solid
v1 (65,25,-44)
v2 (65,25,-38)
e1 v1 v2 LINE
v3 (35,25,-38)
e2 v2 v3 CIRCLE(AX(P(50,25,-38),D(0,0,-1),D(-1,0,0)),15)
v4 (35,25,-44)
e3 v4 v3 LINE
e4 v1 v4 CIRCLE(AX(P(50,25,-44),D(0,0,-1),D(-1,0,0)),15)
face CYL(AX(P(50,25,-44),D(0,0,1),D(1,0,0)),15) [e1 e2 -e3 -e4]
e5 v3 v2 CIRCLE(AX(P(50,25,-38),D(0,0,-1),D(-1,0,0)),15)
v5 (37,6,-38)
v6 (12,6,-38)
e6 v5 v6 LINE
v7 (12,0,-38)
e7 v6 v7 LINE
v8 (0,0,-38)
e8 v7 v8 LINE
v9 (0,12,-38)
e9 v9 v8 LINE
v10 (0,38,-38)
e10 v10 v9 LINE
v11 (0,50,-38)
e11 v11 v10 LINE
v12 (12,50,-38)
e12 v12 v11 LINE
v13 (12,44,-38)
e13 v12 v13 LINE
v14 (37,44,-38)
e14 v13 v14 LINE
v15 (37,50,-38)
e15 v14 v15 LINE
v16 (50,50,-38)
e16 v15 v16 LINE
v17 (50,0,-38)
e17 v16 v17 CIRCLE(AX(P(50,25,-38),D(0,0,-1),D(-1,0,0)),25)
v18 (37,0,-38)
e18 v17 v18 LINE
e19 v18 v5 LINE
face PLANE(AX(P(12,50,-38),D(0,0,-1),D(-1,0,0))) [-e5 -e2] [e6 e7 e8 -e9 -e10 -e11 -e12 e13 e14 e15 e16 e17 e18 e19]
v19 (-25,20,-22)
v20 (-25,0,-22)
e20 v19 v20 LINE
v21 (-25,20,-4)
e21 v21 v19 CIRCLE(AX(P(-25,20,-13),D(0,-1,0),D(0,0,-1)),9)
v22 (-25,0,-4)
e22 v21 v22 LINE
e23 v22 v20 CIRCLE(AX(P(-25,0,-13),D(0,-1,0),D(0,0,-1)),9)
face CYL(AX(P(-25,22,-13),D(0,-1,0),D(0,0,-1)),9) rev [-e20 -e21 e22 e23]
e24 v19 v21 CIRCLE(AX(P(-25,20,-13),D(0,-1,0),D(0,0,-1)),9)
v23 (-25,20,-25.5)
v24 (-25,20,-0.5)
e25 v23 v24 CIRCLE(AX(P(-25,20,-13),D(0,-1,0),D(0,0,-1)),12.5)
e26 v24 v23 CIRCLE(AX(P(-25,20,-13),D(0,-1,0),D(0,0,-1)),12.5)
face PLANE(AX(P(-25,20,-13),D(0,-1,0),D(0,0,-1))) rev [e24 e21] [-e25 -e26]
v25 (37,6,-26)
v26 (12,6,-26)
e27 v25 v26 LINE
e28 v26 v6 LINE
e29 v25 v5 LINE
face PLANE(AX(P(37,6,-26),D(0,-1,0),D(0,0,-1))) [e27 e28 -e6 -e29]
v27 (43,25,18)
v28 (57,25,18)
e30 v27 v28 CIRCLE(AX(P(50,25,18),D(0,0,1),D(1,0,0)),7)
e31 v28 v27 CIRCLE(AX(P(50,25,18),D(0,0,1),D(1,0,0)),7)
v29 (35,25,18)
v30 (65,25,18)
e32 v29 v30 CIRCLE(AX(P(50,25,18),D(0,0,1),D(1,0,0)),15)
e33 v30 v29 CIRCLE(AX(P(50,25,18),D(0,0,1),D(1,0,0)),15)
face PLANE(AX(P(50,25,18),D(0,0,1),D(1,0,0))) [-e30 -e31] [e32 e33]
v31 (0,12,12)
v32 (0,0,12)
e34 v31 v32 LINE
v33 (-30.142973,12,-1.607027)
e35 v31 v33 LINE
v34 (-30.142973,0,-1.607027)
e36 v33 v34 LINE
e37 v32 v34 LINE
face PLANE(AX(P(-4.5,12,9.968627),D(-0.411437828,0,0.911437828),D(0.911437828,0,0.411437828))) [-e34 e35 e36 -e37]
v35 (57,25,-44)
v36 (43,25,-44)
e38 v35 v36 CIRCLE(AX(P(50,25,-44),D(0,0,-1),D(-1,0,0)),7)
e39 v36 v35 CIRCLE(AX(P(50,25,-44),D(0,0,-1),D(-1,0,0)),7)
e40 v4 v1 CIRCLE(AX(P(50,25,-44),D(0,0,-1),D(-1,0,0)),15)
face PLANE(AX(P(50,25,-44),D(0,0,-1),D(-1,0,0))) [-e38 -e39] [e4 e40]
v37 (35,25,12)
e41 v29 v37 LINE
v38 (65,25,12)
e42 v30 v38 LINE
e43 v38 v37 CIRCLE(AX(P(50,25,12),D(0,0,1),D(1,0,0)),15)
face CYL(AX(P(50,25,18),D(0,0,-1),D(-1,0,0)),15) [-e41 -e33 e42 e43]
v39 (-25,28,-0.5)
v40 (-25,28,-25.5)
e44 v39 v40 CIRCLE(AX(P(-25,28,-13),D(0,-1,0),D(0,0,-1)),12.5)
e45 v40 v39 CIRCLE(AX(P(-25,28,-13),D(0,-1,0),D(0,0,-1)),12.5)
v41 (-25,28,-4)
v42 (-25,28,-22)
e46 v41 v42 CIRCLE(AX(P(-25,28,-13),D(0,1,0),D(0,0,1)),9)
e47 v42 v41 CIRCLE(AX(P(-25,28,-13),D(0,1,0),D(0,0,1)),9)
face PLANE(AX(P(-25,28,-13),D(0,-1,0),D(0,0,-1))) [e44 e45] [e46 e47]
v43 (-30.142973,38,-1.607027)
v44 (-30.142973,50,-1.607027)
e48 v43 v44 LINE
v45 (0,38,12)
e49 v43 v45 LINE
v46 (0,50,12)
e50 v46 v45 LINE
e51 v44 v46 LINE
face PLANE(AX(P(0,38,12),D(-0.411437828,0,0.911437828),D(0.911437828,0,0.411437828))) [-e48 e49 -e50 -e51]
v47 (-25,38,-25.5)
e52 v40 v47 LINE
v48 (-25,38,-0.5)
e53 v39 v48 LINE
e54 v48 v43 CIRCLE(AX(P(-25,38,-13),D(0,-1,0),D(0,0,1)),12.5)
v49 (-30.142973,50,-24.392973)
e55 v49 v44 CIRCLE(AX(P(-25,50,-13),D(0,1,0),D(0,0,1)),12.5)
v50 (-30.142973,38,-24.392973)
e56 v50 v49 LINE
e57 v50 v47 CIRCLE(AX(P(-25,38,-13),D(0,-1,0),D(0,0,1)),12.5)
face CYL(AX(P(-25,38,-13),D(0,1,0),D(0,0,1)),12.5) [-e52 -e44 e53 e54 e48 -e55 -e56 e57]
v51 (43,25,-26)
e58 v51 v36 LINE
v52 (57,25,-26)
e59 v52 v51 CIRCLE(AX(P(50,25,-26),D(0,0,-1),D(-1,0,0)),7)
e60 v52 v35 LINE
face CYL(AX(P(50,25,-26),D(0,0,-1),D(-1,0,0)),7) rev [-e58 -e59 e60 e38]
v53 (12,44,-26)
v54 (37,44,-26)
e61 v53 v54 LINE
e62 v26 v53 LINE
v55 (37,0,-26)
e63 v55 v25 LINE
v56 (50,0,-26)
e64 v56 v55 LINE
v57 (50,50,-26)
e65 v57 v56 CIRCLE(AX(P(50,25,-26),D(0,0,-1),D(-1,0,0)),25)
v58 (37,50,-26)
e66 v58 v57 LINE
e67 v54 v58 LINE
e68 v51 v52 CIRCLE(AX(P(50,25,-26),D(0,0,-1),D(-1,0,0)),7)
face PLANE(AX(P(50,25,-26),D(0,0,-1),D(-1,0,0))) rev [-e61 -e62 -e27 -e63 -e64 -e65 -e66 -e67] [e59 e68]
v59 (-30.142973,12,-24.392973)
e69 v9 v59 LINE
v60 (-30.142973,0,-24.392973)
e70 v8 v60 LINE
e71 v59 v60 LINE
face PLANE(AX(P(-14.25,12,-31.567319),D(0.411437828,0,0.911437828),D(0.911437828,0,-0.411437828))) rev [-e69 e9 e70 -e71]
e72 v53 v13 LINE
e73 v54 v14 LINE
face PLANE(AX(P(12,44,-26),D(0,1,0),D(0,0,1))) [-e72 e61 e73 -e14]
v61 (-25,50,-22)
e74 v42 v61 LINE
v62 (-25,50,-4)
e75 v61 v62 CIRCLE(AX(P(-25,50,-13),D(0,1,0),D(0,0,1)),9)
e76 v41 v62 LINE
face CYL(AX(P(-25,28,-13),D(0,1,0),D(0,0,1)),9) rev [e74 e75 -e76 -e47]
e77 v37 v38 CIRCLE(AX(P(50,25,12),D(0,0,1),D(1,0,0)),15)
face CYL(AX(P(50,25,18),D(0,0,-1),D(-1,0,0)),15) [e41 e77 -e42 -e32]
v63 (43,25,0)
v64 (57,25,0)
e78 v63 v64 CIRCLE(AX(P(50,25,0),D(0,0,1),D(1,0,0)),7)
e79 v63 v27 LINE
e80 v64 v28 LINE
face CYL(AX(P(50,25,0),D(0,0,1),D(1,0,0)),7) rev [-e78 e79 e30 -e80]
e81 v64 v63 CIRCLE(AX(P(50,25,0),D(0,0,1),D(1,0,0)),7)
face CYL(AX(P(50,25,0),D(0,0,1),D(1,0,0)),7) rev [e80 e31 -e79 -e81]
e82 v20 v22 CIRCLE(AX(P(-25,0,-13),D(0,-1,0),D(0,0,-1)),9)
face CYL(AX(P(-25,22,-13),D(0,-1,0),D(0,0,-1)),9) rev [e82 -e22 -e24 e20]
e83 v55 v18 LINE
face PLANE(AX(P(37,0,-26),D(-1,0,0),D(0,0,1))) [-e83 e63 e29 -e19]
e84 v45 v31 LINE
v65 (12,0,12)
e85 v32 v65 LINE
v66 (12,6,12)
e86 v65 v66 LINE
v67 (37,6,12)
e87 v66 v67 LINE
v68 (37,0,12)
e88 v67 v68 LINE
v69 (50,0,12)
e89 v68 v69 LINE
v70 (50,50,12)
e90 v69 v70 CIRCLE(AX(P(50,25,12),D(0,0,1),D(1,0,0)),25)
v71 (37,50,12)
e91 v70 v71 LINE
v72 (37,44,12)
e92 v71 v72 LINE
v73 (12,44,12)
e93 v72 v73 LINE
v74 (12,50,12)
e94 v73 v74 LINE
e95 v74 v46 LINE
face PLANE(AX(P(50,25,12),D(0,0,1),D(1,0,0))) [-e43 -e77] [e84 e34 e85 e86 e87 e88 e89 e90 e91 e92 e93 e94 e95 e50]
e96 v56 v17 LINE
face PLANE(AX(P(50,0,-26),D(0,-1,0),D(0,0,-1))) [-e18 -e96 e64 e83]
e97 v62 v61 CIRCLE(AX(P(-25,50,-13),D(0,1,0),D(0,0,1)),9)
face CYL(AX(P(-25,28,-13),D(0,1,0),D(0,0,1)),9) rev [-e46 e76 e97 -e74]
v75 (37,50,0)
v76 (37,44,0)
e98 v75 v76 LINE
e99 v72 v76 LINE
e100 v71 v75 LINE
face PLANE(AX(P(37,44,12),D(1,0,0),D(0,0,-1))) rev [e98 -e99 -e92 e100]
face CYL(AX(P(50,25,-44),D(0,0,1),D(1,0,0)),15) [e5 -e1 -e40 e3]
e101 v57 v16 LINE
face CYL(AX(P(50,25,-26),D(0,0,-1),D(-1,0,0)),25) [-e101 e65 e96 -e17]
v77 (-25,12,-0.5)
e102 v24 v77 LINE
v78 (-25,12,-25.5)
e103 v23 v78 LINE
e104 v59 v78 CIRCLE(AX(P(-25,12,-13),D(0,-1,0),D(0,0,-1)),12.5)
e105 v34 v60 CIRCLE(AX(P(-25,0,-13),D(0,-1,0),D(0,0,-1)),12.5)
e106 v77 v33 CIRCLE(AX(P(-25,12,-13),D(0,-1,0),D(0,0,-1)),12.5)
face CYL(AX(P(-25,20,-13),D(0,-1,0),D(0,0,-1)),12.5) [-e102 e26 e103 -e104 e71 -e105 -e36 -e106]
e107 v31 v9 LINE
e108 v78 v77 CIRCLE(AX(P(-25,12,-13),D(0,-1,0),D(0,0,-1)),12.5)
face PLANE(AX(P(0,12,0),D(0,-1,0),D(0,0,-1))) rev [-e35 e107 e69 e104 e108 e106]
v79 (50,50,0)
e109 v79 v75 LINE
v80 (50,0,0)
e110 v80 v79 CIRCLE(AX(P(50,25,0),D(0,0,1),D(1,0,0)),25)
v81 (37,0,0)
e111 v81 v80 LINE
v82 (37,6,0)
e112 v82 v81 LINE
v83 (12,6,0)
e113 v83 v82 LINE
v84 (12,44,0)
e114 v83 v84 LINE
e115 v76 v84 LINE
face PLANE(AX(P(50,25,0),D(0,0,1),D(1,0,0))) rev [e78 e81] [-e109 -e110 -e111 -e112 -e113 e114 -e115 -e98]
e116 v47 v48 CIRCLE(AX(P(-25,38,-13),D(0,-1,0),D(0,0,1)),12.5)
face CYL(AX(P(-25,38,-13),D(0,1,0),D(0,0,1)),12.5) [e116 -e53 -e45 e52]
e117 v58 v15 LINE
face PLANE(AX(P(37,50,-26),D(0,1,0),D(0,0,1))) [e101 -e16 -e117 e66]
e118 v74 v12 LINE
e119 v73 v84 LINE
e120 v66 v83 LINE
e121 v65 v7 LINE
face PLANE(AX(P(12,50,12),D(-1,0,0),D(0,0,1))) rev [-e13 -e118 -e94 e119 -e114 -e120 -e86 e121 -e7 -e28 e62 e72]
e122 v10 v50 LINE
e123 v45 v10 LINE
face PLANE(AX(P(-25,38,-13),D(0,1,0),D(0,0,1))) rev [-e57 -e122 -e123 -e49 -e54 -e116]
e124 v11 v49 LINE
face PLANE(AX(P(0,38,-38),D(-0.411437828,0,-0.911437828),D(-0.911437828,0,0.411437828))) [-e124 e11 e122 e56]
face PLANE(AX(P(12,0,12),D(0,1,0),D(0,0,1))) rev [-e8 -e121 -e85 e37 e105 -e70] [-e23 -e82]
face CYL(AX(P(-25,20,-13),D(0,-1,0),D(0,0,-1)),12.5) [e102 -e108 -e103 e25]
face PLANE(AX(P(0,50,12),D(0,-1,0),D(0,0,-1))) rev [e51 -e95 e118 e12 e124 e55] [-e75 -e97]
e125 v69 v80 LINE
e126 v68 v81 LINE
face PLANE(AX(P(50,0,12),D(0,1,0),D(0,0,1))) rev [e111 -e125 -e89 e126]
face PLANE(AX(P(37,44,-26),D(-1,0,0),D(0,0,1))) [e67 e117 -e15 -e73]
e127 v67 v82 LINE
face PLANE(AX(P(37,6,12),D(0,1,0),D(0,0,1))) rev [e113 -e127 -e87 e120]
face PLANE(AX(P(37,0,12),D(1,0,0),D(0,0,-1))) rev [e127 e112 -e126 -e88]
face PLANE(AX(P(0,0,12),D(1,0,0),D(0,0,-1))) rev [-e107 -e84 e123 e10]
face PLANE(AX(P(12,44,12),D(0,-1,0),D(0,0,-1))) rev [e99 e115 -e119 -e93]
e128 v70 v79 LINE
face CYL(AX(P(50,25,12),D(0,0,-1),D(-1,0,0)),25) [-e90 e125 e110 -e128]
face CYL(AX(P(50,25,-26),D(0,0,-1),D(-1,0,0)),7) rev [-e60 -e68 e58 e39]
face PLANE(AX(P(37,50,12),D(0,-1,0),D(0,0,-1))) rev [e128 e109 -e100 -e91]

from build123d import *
from build123d.topology import SkipClean

# Parameters (mm, degrees)
MAIN_BODY_PLATE_DEPTH   = 12
UPPER_HUB_SKETCH_R      = 15
UPPER_HUB_30_DEPTH      = 6
SPACER_BLOCK_SKETCH_W   = 38
SPACER_BLOCK_SKETCH_H   = 50
SPACER_BLOCK_DEPTH      = 12
LOWER_LUG_DEPTH         = 12
LOWER_START             = 6
LOWER_HUB_SKETCH_R      = 15
LOWER_HUB_30_DEPTH      = 6
LOWER_PIN_BORE_SKETCH_R = 7
LOWER_PIN_BORE_14_DEPTH = 18
UPPER_START             = -18
UPPER_PIN_BORE_SKETCH_R = 7
UPPER_PIN_BORE_14_DEPTH = 18
CLEVIS_PLATE_DEPTH      = 12
CLEVIS_HUB_SKETCH_R     = 12.5
CLEVIS_HUB_25_DEPTH     = 10
CLEVIS_START            = -12
CLEVIS_WEB_DEPTH        = 12
CLEVIS_START_2          = -20
CLEVIS_LUG_SKETCH_R     = 12.5
CLEVIS_LUG_25_DEPTH     = 20
CLEVIS_BORE_A_SKETCH_R  = 9
CLEVIS_BORE_A_18_DEPTH  = 22
CLEVIS_START_3          = -22
CLEVIS_BORE_B_SKETCH_R  = 9
CLEVIS_BORE_B_18_DEPTH  = 22


with BuildPart() as part:
    # Main Body Profile Sketch → Main Body Plate (new body)
    with BuildSketch(Plane.XY):
        with BuildLine():
            Line((0, 0), (0, 50))
            Line((0, 50), (12, 50))
            Line((12, 50), (12, 44))
            Line((12, 44), (37, 44))
            Line((37, 44), (37, 50))
            Line((37, 50), (50, 50))
            ThreePointArc((50, 50), (75, 25), (50, 0))
            Line((50, 0), (37, 0))
            Line((37, 0), (37, 6))
            Line((37, 6), (12, 6))
            Line((12, 6), (12, 0))
            Line((12, 0), (0, 0))
        make_face()
    extrude(amount=MAIN_BODY_PLATE_DEPTH)

    # Upper Hub Sketch → Upper Hub Ø30 (add)
    with BuildSketch(Plane.XY.offset(12)):
        with Locations((50, 25)):
            Circle(UPPER_HUB_SKETCH_R)
    extrude(amount=UPPER_HUB_30_DEPTH)

    # Spacer Block Sketch → Spacer Block (add)
    with BuildSketch(Plane.ZY):
        with Locations((-19, 25)):
            Rectangle(SPACER_BLOCK_SKETCH_W, SPACER_BLOCK_SKETCH_H)
    extrude(amount=-SPACER_BLOCK_DEPTH)

    # Lower Lug Sketch → Lower Lug (add)
    with BuildSketch(Plane(origin=(0, 0, -38), x_dir=(-1, 0, 0), z_dir=(0, 0, -1))):
        with BuildLine():
            Line((-12, 44), (-37, 44))
            Line((-37, 44), (-37, 50))
            Line((-37, 50), (-50, 50))
            ThreePointArc((-50, 50), (-75, 25), (-50, 0))
            Line((-50, 0), (-37, 0))
            Line((-37, 0), (-37, 6))
            Line((-37, 6), (-12, 6))
            Line((-12, 6), (-12, 44))
        make_face()
    extrude(amount=-LOWER_LUG_DEPTH)

    # Lower Hub Sketch → Lower Hub Ø30 (add)
    with BuildSketch(Plane(origin=(0, 0, -38), x_dir=(-1, 0, 0), z_dir=(0, 0, -1)).offset(LOWER_START)):
        with Locations(Location((-50, 25, 0), (0, 0, 180))):
            Circle(LOWER_HUB_SKETCH_R)
    extrude(amount=-LOWER_HUB_30_DEPTH)

    # Lower Pin Bore Sketch → Lower Pin Bore Ø14 (cut)
    with BuildSketch(Plane(origin=(0, 0, -44), x_dir=(-1, 0, 0), z_dir=(0, 0, -1))):
        with Locations((-50, 25)):
            Circle(LOWER_PIN_BORE_SKETCH_R)
    extrude(amount=-LOWER_PIN_BORE_14_DEPTH, mode=Mode.SUBTRACT)

    # Upper Pin Bore Sketch → Upper Pin Bore Ø14 (cut)
    with BuildSketch(Plane.XY.offset(18).offset(UPPER_START)):
        with Locations(Location((50, 25, 0), (0, 0, 180))):
            Circle(UPPER_PIN_BORE_SKETCH_R)
    extrude(amount=UPPER_PIN_BORE_14_DEPTH, mode=Mode.SUBTRACT)

    # Clevis Plate Sketch → Clevis Plate (add)
    with BuildSketch(Plane(origin=(0, 50, 0), x_dir=(1, 0, 0), z_dir=(0, 1, 0))):
        with BuildLine():
            Line((0, 38), (-30.142972847, 24.392972847))
            ThreePointArc((-30.142972847, 24.392972847), (-37.5, 13), (-30.142972847, 1.607027153))
            Line((-30.142972847, 1.607027153), (0, -12))
            Line((0, -12), (0, 38))
        make_face()
    extrude(amount=-CLEVIS_PLATE_DEPTH)

    # Clevis Hub Sketch → Clevis Hub Ø25 (add)
    with SkipClean():  # the faces are left unmerged after this step: merging them gives an invalid solid
        with BuildSketch(Plane.XZ.offset(-38)):
            with Locations(Location((-25, -13, 0), (0, 0, 114.295188945))):
                Circle(CLEVIS_HUB_SKETCH_R)
        extrude(amount=CLEVIS_HUB_25_DEPTH)

    # Clevis Web Sketch → Clevis Web (add)
    with SkipClean():  # the faces are left unmerged after this step: merging them gives an invalid solid
        with BuildSketch(Plane.XZ.offset(CLEVIS_START)):
            with BuildLine():
                Line((0, -38), (0, 12))
                Line((0, 12), (-30.142972847, -1.607027153))
                ThreePointArc((-30.142972847, -1.607027153), (-18.219039913, -2.499115261), (-12.5, -13))
                ThreePointArc((-12.5, -13), (-18.219039913, -23.500884739), (-30.142972847, -24.392972847))
                Line((-30.142972847, -24.392972847), (0, -38))
            make_face()
        extrude(amount=CLEVIS_WEB_DEPTH)

    # Clevis Lug Sketch → Clevis Lug Ø25 (add)
    with SkipClean():  # the faces are left unmerged after this step: merging them gives an invalid solid
        with BuildSketch(Plane.XZ.offset(CLEVIS_START_2)):
            with Locations(Location((-25, -13, 0), (0, 0, 114.295188945))):
                Circle(CLEVIS_LUG_SKETCH_R)
        extrude(amount=CLEVIS_LUG_25_DEPTH)

    # Clevis Bore A Sketch → Clevis Bore A Ø18 (cut)
    with SkipClean():  # the faces are left unmerged after this step: merging them gives an invalid solid
        with BuildSketch(Plane(origin=(0, 50, 0), x_dir=(1, 0, 0), z_dir=(0, 1, 0))):
            with Locations(Location((-25, 13, 0), (0, 0, 270))):
                Circle(CLEVIS_BORE_A_SKETCH_R)
        extrude(amount=-CLEVIS_BORE_A_18_DEPTH, mode=Mode.SUBTRACT)

    # Clevis Bore B Sketch → Clevis Bore B Ø18 (cut)
    with SkipClean():  # the faces are left unmerged after this step: merging them gives an invalid solid
        with BuildSketch(Plane.XZ.offset(CLEVIS_START_3)):
            with Locations(Location((-25, -13, 0), (0, 0, 90))):
                Circle(CLEVIS_BORE_B_SKETCH_R)
        extrude(amount=CLEVIS_BORE_B_18_DEPTH, mode=Mode.SUBTRACT)


solid = part.part
